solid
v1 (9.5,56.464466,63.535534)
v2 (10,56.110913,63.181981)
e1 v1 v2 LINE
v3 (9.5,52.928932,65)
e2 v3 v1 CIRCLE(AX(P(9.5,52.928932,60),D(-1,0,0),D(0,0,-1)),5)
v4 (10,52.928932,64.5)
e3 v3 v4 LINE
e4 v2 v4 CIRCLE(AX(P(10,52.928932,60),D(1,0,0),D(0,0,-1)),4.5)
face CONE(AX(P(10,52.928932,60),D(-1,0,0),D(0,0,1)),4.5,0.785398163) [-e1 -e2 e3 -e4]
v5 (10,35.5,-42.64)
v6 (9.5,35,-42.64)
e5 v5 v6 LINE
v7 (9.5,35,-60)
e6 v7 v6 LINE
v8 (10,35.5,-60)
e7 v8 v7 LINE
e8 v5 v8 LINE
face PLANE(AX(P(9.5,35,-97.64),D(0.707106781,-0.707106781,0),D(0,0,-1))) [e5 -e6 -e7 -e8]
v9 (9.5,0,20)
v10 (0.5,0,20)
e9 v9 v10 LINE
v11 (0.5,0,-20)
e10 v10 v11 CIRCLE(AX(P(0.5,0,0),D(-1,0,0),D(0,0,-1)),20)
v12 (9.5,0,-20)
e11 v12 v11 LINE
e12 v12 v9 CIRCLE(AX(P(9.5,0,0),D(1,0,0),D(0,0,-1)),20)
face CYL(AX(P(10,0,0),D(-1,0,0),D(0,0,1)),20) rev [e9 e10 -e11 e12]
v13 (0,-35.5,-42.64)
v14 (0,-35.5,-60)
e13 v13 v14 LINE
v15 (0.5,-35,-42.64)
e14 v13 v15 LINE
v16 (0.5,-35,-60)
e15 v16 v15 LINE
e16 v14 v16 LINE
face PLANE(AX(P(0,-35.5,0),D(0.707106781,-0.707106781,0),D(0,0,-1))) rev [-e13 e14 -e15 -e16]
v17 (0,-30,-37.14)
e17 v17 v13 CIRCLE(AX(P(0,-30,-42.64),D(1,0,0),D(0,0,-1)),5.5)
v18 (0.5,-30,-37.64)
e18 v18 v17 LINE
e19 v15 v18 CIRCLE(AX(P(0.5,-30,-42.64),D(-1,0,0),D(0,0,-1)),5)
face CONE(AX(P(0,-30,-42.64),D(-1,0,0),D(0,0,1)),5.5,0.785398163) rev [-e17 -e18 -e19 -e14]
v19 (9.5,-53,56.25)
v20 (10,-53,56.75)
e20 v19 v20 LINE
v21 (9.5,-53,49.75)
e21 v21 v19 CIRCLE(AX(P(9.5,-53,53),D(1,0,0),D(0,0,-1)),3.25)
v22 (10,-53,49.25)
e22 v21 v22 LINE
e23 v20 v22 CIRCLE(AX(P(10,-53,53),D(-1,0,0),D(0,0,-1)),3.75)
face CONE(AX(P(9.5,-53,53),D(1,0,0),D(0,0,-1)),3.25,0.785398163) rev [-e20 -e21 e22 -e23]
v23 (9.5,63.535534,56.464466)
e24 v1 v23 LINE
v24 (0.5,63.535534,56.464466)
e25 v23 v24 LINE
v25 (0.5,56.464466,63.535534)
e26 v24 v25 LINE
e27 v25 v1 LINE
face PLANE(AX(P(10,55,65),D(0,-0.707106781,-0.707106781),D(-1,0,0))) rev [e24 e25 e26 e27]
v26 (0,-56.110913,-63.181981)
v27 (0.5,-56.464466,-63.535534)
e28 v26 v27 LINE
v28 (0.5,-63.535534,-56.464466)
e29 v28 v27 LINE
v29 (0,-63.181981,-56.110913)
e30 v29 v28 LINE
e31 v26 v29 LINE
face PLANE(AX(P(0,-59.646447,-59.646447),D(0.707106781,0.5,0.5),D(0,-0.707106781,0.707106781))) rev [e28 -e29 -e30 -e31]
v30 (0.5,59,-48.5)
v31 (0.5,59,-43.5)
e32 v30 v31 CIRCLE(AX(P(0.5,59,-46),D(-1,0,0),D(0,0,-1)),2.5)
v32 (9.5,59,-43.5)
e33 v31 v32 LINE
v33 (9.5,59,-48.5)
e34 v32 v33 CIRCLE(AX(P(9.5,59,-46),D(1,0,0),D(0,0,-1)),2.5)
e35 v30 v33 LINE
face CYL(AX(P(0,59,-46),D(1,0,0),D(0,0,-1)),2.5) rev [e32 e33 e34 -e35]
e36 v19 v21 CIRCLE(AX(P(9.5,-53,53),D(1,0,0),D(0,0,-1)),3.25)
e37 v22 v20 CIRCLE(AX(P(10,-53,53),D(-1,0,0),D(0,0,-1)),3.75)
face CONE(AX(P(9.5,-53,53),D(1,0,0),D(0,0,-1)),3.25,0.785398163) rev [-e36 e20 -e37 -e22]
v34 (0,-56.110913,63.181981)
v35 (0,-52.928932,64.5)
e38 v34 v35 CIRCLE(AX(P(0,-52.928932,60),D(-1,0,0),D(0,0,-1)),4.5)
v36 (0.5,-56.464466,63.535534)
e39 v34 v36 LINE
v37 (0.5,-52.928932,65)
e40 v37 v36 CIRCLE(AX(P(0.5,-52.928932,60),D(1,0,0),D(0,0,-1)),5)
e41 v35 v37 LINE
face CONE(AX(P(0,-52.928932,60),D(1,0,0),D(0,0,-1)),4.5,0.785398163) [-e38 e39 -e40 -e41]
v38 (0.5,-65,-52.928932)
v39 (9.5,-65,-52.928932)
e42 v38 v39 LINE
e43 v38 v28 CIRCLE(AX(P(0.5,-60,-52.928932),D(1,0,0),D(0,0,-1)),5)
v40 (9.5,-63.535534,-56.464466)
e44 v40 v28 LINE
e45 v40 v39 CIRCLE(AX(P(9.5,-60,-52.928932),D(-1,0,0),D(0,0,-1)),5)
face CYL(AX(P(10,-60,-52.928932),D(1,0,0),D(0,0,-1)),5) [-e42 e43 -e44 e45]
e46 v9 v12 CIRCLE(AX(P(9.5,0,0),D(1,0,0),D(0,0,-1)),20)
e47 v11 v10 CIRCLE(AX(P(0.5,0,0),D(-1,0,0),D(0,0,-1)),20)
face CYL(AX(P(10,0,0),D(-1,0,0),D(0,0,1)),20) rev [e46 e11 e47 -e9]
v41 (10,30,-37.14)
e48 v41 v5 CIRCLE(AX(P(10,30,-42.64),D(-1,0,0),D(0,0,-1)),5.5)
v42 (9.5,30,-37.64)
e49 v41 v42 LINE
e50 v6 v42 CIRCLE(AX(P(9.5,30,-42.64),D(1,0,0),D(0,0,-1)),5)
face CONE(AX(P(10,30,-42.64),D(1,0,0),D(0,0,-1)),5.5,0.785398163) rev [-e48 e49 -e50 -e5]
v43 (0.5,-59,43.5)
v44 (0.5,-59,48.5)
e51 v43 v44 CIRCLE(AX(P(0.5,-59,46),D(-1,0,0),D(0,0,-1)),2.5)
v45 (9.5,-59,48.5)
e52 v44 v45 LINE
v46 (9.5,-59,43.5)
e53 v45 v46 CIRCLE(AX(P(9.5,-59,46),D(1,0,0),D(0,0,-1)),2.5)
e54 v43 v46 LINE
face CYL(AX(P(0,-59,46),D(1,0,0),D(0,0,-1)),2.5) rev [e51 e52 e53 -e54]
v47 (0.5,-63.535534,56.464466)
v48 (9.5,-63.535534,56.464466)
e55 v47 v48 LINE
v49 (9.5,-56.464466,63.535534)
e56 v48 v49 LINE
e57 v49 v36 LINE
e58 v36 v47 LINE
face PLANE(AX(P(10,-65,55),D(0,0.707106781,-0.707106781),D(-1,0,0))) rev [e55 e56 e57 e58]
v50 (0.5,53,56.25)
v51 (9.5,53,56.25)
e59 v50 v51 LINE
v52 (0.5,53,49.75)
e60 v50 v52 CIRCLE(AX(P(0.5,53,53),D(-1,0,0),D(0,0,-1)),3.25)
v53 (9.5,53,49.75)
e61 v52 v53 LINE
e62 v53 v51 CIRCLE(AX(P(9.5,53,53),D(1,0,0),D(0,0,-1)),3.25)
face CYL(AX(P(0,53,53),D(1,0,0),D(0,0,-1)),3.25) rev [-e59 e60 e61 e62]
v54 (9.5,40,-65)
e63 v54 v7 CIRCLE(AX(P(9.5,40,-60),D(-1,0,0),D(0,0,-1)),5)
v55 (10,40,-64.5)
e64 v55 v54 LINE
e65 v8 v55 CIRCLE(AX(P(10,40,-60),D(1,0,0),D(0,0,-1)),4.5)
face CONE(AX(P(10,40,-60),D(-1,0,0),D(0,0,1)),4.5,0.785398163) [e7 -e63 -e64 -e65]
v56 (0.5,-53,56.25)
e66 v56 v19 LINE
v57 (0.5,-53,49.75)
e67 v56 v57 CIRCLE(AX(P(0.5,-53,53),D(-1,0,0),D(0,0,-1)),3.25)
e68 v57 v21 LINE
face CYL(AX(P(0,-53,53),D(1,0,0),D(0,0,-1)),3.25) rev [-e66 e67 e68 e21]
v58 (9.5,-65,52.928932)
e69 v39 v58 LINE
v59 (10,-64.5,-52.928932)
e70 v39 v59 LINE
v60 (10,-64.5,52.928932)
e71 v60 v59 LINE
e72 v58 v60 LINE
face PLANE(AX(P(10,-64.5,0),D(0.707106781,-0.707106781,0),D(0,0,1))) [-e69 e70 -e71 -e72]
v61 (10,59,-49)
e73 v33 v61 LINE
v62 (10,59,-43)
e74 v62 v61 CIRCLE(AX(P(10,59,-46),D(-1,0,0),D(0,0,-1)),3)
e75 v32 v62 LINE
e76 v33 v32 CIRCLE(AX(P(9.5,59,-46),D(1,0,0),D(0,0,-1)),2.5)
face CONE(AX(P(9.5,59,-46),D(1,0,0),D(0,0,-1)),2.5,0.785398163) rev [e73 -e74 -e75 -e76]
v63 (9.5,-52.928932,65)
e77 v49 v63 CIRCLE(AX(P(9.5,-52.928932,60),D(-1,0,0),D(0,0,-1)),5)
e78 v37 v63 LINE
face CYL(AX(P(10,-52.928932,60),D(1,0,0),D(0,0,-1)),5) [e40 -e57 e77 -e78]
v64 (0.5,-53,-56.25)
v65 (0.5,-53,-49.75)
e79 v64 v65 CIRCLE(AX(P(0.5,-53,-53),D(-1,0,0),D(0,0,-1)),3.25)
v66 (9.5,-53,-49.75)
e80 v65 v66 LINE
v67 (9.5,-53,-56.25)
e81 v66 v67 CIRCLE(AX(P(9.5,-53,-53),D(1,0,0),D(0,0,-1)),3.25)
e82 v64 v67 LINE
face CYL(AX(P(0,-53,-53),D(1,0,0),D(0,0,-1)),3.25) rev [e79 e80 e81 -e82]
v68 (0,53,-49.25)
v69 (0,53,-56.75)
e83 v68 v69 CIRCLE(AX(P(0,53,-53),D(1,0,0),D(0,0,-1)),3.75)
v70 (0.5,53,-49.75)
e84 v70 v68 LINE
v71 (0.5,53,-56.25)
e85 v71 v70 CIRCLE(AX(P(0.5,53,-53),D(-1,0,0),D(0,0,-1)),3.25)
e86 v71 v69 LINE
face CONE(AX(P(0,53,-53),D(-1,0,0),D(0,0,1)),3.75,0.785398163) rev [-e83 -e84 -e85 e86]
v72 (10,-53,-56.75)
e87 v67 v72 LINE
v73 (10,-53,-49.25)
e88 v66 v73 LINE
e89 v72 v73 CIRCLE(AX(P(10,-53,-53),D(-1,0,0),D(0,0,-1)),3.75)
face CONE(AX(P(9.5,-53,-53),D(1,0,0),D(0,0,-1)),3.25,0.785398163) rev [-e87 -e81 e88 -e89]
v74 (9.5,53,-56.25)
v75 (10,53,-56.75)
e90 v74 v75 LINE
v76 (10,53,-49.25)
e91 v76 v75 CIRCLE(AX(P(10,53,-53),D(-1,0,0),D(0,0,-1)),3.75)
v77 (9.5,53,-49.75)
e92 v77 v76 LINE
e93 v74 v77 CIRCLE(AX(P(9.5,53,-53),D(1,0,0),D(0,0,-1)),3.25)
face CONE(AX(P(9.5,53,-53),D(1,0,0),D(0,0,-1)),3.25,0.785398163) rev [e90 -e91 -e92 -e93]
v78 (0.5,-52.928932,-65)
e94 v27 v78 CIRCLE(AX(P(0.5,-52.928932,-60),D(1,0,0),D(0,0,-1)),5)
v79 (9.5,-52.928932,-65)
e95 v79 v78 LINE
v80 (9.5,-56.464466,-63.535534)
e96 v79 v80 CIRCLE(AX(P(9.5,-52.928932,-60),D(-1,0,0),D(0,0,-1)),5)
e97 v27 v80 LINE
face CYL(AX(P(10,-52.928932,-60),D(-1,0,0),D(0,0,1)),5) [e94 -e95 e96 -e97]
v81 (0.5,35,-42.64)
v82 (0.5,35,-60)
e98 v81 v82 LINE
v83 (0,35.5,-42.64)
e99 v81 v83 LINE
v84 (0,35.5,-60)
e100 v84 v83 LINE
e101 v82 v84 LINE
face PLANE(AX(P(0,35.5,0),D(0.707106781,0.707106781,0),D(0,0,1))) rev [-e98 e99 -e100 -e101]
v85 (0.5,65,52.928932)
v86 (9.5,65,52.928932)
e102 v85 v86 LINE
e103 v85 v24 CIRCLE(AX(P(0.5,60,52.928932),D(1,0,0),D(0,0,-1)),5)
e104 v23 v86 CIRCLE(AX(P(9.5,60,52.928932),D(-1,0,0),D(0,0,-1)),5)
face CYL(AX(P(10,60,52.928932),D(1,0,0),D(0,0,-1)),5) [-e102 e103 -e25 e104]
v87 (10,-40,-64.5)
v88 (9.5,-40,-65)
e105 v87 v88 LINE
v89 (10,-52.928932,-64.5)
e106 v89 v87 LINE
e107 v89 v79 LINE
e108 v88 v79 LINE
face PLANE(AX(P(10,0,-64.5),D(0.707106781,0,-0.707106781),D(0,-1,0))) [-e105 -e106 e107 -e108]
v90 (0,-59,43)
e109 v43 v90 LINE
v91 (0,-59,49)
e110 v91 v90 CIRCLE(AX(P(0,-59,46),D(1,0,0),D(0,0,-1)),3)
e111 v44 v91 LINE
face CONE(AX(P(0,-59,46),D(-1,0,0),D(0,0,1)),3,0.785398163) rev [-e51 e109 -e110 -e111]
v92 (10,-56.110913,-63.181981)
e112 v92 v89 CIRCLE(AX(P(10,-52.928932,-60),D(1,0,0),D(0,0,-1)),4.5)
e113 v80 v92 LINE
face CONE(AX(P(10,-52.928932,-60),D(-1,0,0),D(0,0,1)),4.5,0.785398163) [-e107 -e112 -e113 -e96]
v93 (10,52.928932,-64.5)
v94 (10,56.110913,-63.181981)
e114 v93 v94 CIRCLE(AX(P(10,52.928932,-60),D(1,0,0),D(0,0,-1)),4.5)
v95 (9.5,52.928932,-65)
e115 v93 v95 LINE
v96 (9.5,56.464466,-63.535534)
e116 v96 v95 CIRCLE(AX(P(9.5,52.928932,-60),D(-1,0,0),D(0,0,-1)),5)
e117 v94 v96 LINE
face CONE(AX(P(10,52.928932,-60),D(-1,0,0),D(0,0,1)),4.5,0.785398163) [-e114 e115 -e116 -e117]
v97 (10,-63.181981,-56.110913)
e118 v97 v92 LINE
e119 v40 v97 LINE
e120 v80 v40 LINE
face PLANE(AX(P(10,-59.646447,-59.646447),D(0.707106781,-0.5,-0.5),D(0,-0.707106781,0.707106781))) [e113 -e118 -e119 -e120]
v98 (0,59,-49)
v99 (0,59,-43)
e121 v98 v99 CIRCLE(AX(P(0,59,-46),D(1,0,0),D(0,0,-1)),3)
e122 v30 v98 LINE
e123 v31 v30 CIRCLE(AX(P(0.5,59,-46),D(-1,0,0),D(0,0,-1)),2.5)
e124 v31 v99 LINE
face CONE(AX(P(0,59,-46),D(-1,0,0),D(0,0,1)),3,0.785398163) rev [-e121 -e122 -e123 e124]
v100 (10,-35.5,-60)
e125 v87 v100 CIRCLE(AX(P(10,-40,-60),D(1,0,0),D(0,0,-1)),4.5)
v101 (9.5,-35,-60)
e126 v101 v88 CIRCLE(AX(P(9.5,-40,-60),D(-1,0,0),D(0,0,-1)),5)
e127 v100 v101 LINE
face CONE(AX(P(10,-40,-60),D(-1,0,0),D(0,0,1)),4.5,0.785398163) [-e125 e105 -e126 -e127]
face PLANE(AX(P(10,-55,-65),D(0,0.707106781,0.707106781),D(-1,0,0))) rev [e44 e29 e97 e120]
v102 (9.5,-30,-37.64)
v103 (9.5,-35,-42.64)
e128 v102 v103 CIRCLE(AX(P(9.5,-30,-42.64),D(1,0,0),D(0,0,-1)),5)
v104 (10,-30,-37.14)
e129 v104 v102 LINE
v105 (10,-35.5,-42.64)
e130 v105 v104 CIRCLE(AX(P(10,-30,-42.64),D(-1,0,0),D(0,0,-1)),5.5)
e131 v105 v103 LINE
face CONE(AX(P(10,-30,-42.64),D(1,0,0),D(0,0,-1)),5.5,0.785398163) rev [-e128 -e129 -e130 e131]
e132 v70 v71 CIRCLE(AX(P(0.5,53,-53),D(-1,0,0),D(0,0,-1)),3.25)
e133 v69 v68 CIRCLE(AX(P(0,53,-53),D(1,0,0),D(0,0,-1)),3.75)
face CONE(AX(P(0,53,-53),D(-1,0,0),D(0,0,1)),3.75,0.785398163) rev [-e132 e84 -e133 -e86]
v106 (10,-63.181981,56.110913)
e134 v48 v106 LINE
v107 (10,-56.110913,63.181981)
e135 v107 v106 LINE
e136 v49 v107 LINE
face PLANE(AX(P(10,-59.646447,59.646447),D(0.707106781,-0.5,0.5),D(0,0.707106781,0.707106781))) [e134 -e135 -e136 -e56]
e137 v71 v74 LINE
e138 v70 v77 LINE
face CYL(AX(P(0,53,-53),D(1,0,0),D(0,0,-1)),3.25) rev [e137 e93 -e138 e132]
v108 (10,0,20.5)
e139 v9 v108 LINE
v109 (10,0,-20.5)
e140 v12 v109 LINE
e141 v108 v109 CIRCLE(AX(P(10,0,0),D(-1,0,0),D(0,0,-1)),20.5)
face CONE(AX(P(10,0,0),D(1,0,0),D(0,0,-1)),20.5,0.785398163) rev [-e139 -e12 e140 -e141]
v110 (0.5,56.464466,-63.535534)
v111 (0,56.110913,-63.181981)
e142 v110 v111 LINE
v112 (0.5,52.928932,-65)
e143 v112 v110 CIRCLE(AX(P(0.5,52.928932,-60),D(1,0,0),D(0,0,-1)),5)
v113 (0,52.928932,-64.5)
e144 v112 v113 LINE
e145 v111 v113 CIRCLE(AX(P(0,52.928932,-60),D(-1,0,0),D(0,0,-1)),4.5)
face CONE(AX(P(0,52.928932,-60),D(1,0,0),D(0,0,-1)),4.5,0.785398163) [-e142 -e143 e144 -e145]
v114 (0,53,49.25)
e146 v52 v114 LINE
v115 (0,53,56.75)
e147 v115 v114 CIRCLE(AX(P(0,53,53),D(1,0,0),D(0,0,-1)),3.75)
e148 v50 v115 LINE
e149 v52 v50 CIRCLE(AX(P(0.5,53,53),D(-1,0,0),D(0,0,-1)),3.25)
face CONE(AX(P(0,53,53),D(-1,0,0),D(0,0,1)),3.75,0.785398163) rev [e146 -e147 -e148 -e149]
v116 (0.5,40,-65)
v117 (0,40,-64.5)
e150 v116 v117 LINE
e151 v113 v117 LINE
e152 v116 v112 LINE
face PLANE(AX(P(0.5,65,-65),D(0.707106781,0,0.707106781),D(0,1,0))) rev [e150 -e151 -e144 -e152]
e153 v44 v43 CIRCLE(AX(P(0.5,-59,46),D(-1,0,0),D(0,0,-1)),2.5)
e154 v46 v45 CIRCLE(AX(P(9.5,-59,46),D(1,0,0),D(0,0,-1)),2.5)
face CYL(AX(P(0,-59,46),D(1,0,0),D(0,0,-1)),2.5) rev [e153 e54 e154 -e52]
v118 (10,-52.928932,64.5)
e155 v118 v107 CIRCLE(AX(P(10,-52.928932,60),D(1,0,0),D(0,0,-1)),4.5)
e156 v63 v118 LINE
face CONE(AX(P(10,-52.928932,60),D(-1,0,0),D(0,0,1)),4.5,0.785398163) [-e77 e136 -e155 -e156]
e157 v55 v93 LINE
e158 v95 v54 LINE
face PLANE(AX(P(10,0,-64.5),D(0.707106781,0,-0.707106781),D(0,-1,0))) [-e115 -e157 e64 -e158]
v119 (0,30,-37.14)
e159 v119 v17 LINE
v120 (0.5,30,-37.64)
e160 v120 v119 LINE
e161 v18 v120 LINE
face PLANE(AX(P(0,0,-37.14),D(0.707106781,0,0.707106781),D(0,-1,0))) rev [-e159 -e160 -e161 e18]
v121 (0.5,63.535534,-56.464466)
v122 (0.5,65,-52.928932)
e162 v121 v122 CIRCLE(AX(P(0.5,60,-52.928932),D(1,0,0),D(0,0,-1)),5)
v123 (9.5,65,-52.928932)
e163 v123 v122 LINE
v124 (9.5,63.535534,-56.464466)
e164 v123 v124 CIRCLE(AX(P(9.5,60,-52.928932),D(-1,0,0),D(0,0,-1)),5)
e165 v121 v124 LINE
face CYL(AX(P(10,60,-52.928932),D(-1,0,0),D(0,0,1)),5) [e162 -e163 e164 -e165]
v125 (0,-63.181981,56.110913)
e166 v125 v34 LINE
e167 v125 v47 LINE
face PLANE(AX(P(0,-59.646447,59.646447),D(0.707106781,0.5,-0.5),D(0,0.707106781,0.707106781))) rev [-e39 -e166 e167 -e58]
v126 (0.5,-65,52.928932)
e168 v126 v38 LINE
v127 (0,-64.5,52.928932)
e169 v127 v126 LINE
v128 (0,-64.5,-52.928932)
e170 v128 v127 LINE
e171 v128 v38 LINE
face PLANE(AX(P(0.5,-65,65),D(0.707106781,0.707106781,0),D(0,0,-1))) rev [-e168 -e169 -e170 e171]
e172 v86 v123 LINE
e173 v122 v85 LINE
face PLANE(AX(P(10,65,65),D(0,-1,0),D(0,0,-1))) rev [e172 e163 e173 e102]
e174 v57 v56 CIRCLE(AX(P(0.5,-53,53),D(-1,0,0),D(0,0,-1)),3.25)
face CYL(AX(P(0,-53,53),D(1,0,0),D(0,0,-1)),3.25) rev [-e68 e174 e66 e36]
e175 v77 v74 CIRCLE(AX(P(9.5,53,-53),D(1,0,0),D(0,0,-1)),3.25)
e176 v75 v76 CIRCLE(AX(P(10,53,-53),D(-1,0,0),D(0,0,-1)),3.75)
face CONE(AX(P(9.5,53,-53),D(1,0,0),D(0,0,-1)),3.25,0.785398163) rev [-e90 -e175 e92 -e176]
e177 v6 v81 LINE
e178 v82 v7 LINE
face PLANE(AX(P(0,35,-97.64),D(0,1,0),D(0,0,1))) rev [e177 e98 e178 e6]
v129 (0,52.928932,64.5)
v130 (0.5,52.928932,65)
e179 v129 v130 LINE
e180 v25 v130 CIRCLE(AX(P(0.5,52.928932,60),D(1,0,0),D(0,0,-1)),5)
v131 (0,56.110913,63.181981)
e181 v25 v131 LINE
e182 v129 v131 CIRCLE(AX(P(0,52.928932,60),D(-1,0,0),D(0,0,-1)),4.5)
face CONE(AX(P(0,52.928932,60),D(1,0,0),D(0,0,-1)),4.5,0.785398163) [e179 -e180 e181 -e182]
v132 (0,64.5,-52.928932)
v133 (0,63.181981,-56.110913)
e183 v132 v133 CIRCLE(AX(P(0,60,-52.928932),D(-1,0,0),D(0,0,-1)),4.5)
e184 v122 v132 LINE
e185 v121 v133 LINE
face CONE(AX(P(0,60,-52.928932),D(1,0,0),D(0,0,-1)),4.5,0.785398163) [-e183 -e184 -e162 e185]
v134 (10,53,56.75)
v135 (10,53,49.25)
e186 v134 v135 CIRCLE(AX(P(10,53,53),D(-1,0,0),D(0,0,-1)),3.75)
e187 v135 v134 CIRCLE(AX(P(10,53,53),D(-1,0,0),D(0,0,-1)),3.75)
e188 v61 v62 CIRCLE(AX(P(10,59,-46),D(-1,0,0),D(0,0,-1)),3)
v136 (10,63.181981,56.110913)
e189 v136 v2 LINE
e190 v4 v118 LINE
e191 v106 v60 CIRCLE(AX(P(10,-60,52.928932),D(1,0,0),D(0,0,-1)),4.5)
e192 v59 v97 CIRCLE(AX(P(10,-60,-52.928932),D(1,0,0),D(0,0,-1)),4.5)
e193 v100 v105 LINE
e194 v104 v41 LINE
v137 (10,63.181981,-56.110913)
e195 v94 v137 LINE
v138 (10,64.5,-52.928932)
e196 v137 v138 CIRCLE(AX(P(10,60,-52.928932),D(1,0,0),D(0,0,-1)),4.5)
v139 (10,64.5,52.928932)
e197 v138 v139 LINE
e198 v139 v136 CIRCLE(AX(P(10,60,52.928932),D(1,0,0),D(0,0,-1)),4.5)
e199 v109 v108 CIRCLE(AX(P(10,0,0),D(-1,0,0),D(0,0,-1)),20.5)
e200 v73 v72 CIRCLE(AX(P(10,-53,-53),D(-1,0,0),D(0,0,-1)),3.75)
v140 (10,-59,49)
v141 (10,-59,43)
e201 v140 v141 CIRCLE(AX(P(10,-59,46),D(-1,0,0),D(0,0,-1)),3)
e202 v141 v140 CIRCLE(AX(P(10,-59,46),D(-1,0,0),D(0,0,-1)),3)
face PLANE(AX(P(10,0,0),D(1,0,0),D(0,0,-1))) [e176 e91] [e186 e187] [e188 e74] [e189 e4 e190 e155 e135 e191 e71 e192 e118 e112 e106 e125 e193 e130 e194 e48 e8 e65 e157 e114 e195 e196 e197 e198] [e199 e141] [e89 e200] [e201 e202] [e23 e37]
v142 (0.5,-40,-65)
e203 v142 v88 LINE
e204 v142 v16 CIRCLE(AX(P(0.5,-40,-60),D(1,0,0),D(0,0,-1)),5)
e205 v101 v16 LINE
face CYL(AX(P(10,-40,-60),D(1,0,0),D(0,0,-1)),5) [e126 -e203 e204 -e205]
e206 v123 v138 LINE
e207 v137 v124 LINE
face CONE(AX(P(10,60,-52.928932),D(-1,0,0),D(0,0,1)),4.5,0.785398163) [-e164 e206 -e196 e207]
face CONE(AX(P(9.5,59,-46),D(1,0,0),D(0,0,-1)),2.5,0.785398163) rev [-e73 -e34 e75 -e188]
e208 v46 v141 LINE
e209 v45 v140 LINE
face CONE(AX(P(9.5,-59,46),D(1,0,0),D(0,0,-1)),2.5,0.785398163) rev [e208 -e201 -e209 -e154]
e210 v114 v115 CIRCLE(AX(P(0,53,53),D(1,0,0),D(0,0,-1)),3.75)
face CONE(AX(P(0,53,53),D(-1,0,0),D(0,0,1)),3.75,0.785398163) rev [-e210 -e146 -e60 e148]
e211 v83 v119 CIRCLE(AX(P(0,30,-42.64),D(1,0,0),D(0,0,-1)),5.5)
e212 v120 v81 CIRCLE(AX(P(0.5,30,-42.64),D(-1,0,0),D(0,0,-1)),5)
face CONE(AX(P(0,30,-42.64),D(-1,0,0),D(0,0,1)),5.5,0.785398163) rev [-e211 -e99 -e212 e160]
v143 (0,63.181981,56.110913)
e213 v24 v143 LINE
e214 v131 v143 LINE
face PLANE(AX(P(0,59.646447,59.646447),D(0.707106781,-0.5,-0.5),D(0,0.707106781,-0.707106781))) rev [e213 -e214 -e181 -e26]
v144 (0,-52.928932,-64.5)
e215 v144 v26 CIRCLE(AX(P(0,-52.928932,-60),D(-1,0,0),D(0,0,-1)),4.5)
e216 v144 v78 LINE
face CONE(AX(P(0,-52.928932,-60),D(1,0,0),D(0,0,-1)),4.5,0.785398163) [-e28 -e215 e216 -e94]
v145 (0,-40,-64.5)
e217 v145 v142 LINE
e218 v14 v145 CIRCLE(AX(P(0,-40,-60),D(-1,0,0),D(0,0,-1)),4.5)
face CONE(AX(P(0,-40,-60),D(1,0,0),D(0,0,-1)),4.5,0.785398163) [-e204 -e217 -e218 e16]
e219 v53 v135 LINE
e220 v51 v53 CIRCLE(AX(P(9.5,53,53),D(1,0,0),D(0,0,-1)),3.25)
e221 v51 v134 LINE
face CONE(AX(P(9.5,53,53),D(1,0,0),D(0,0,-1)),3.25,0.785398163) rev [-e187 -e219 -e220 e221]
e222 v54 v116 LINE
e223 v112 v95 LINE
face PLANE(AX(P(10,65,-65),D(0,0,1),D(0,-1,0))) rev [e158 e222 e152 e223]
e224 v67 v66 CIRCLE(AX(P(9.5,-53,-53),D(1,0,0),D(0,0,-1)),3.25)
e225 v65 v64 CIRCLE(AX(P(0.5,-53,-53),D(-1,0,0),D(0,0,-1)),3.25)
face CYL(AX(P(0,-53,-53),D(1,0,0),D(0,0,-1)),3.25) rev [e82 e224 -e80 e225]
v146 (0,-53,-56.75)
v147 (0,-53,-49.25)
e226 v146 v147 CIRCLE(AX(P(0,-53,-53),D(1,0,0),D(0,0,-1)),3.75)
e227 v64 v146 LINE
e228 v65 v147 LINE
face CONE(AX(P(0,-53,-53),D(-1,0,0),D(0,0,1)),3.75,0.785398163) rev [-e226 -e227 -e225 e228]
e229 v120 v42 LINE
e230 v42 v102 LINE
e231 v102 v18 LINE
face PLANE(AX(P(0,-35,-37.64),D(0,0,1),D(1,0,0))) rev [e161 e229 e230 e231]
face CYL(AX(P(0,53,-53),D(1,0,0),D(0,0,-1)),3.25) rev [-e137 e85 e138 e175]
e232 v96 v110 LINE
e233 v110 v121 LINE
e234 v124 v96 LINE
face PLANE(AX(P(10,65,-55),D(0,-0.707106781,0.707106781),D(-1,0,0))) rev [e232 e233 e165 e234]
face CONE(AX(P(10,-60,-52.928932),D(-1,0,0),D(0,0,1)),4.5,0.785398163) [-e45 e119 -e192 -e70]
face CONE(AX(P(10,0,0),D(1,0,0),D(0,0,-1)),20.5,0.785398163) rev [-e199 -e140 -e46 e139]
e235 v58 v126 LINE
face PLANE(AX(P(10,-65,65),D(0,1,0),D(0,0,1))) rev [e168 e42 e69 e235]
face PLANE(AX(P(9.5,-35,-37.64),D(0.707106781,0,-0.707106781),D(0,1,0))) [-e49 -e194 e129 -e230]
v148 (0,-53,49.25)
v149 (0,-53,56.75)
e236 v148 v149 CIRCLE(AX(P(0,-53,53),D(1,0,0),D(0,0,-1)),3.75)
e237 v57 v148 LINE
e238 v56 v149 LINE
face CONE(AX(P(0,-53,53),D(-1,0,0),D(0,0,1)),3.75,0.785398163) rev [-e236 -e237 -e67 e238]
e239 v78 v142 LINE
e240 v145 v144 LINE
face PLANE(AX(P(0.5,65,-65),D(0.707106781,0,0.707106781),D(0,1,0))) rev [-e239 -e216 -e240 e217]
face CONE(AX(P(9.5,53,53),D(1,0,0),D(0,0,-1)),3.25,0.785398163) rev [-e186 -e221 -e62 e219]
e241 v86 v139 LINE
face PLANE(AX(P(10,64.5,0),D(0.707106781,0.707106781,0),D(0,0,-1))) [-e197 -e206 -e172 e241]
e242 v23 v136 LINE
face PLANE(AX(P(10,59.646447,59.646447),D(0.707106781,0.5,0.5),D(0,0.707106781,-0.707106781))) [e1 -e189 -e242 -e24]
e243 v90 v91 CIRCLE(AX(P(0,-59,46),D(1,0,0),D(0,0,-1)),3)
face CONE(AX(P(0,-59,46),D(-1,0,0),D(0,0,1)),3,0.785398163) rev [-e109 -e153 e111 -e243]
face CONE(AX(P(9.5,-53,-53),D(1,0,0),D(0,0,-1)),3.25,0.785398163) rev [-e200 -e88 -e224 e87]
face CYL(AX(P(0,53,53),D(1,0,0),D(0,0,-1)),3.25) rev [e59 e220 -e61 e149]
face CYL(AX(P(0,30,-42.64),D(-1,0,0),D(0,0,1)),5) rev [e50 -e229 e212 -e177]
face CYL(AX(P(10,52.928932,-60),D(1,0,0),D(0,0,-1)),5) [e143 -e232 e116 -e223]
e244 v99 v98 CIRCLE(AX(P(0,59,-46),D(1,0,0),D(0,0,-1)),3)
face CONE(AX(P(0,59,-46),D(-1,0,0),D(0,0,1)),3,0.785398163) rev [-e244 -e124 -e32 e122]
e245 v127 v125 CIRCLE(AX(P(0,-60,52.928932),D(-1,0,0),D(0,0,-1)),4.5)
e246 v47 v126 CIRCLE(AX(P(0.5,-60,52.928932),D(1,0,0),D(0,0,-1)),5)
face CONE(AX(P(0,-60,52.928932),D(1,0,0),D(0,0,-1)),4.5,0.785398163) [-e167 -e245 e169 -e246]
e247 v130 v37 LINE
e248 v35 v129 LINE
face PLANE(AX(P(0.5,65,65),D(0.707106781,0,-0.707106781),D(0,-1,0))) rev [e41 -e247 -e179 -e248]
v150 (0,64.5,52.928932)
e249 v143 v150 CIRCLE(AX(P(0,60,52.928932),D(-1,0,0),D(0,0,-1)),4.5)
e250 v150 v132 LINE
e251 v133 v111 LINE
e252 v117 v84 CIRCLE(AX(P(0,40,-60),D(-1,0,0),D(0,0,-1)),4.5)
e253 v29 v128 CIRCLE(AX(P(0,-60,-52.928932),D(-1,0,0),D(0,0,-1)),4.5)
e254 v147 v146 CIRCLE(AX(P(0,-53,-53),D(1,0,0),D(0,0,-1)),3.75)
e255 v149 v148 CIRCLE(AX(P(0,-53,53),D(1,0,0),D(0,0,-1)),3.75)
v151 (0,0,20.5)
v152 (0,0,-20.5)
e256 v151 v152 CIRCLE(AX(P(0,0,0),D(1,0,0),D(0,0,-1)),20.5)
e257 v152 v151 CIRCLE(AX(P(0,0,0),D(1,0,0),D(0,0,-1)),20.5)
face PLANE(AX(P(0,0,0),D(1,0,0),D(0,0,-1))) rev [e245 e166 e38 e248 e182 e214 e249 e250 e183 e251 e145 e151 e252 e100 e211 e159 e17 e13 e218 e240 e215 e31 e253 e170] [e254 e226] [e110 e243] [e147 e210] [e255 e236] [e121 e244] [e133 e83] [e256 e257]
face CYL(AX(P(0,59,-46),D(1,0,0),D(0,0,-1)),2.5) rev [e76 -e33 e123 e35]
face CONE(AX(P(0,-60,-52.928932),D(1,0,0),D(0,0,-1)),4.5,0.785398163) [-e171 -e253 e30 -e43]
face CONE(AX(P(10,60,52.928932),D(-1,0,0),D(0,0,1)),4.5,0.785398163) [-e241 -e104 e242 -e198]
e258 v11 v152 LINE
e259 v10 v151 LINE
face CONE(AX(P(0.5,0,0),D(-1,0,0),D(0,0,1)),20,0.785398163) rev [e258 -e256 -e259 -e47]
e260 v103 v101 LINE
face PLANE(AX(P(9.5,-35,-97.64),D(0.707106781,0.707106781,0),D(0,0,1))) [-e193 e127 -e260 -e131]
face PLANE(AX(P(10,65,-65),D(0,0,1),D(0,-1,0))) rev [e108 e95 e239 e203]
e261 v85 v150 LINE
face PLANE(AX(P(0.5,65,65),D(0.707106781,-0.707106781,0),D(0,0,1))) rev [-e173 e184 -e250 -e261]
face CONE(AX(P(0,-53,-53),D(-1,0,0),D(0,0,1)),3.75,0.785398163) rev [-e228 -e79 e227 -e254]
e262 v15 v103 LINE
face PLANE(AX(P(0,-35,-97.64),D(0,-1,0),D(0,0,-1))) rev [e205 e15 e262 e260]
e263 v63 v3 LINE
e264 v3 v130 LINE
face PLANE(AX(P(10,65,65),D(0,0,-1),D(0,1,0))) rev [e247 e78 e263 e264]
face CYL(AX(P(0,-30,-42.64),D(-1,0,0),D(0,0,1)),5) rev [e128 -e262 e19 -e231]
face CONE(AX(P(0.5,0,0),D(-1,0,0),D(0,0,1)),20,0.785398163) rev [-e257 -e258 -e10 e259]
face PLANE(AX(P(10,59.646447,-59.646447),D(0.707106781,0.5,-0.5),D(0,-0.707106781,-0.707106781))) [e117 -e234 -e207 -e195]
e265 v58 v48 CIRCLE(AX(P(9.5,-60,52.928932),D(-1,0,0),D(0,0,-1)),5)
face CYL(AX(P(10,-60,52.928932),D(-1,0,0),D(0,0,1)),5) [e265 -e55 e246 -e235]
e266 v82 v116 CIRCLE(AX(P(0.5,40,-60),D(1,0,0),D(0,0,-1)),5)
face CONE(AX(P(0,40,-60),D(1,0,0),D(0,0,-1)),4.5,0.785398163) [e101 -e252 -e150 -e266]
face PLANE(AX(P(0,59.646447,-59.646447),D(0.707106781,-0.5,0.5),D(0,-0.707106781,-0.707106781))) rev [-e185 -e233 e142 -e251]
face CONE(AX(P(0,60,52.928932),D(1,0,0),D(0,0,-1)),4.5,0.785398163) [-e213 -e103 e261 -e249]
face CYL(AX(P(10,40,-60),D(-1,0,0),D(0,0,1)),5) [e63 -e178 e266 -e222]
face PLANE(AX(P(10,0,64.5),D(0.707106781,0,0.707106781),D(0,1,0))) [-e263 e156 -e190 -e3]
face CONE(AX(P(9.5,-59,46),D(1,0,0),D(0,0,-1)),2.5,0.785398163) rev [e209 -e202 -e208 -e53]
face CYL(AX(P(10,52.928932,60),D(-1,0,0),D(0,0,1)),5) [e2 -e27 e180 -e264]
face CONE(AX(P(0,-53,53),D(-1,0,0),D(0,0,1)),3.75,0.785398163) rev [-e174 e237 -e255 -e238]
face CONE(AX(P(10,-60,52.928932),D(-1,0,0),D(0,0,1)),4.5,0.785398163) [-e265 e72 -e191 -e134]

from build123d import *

# Parameters (mm, degrees)
SKETCH_1_W          = 130
SKETCH_1_H          = 130
EXTRUDE_1_DEPTH     = 10
SKETCH_2_W          = 60
SKETCH_2_H          = 70
CUT_EXTRUDE_1_DEPTH = 93.466210045
CHAMFER_1_SIZE      = 10
SKETCH_3_R          = 3.25
CUT_EXTRUDE_2_DEPTH = 93.466210045
SKETCH_4_R          = 2.5
CUT_EXTRUDE_3_DEPTH = 93.466210045
SKETCH_5_R          = 20
CUT_EXTRUDE_6_DEPTH = 93.466210045
FILLET_1_R          = 5
FILLET_2_R          = 5
CHAMFER_2_SIZE      = 0.5


with BuildPart() as part:
    # 草图1 → 凸台-拉伸1 (new body)
    with BuildSketch(Plane(origin=(0, 0, 0), x_dir=(0, 0, -1), z_dir=(1, 0, 0))):
        Rectangle(SKETCH_1_W, SKETCH_1_H)
    extrude(amount=EXTRUDE_1_DEPTH)

    # 草图2 → 切除-拉伸1 (cut, through all)
    with BuildSketch(Plane(origin=(10, 0, 0), x_dir=(0, 0, -1), z_dir=(1, 0, 0))):
        with Locations((67.64, 0)):
            Rectangle(SKETCH_2_W, SKETCH_2_H)
    extrude(amount=-CUT_EXTRUDE_1_DEPTH, mode=Mode.SUBTRACT)

    # 倒角1
    chamfer_1_edges = [part.edges().sort_by_distance(p)[0] for p in [
        (5, -65, -65),
        (5, -65, 65),
        (5, 65, 65),
        (5, 65, -65),
    ]]
    chamfer(chamfer_1_edges, length=CHAMFER_1_SIZE)

    # 草图3 → 切除-拉伸2 (cut, through all)
    with BuildSketch(Plane(origin=(10, 0, 0), x_dir=(0, 0, -1), z_dir=(1, 0, 0))):
        with Locations((-53, -53)):
            Circle(SKETCH_3_R)
        with Locations((-53, 53)):
            Circle(SKETCH_3_R)
        with Locations((53, -53)):
            Circle(SKETCH_3_R)
        with Locations((53, 53)):
            Circle(SKETCH_3_R)
    extrude(amount=-CUT_EXTRUDE_2_DEPTH, mode=Mode.SUBTRACT)

    # 草图4 → 切除-拉伸3 (cut, through all)
    with BuildSketch(Plane(origin=(10, 0, 0), x_dir=(0, 0, -1), z_dir=(1, 0, 0))):
        with Locations((-46, -59)):
            Circle(SKETCH_4_R)
        with Locations((46, 59)):
            Circle(SKETCH_4_R)
    extrude(amount=-CUT_EXTRUDE_3_DEPTH, mode=Mode.SUBTRACT)

    # 草图5 → 切除-拉伸6 (cut, through all)
    with BuildSketch(Plane.ZY):
        Circle(SKETCH_5_R)
    extrude(amount=-CUT_EXTRUDE_6_DEPTH, mode=Mode.SUBTRACT)

    # 圆角1
    fillet_1_edges = [part.edges().sort_by_distance(p)[0] for p in [
        (5, 35, -37.64),
        (5, -35, -37.64),
    ]]
    fillet(fillet_1_edges, radius=FILLET_1_R)

    # 圆角2
    fillet_2_edges = [part.edges().sort_by_distance(p)[0] for p in [
        (5, -35, -65),
        (5, 35, -65),
        (5, 65, 55),
        (5, 65, -55),
        (5, 55, -65),
        (5, -55, -65),
        (5, -65, 55),
        (5, -65, -55),
        (5, -55, 65),
        (5, 55, 65),
    ]]
    fillet(fillet_2_edges, radius=FILLET_2_R)

    # 倒角2
    chamfer_2_edges = [part.edges().sort_by_distance(p)[0] for p in [
        (10, 65, 0),
        (0, 65, 0),
        (10, 46.464466094, -65),
        (10, 60, -60),
        (10, 60, 60),
        (10, 0, 65),
        (10, -60, 60),
        (10, -65, 0),
        (10, -60, -60),
        (10, -46.464466094, -65),
        (10, 35, -51.32),
        (10, -64.619397663, 54.84234935),
        (10, -54.84234935, 64.619397663),
        (10, 64.619397663, -54.84234935),
        (10, 54.84234935, -64.619397663),
        (10, 36.464466094, -63.535533906),
        (10, -36.464466094, -63.535533906),
        (10, -54.84234935, -64.619397663),
        (10, -64.619397663, -54.84234935),
        (10, 54.84234935, 64.619397663),
        (10, 64.619397663, 54.84234935),
        (0, 60, 60),
        (0, 60, -60),
        (0, 46.464466094, -65),
        (0, 35, -51.32),
        (0, -46.464466094, -65),
        (0, -60, -60),
        (0, -65, 0),
        (0, -60, 60),
        (0, 0, 65),
        (0, -64.619397663, 54.84234935),
        (0, -54.84234935, 64.619397663),
        (0, 64.619397663, -54.84234935),
        (0, 54.84234935, -64.619397663),
        (0, 36.464466094, -63.535533906),
        (0, -36.464466094, -63.535533906),
        (0, -54.84234935, -64.619397663),
        (0, -64.619397663, -54.84234935),
        (0, 54.84234935, 64.619397663),
        (0, 64.619397663, 54.84234935),
        (0, -53, 56.25),
        (10, -53, 56.25),
        (0, 53, 56.25),
        (10, 53, 56.25),
        (0, -53, -49.75),
        (10, -53, -49.75),
        (0, 53, -49.75),
        (10, 53, -49.75),
        (0, -59, 48.5),
        (10, -59, 48.5),
        (0, 59, -43.5),
        (10, 59, -43.5),
        (10, 0, -20),
        (0, 0, -20),
        (0, -35, -51.32),
        (10, -35, -51.32),
        (10, 0, -37.64),
        (0, 0, -37.64),
        (10, -33.535533906, -39.104466094),
        (0, -33.535533906, -39.104466094),
        (10, 33.535533906, -39.104466094),
        (0, 33.535533906, -39.104466094),
    ]]
    chamfer(chamfer_2_edges, length=CHAMFER_2_SIZE)


solid = part.part
